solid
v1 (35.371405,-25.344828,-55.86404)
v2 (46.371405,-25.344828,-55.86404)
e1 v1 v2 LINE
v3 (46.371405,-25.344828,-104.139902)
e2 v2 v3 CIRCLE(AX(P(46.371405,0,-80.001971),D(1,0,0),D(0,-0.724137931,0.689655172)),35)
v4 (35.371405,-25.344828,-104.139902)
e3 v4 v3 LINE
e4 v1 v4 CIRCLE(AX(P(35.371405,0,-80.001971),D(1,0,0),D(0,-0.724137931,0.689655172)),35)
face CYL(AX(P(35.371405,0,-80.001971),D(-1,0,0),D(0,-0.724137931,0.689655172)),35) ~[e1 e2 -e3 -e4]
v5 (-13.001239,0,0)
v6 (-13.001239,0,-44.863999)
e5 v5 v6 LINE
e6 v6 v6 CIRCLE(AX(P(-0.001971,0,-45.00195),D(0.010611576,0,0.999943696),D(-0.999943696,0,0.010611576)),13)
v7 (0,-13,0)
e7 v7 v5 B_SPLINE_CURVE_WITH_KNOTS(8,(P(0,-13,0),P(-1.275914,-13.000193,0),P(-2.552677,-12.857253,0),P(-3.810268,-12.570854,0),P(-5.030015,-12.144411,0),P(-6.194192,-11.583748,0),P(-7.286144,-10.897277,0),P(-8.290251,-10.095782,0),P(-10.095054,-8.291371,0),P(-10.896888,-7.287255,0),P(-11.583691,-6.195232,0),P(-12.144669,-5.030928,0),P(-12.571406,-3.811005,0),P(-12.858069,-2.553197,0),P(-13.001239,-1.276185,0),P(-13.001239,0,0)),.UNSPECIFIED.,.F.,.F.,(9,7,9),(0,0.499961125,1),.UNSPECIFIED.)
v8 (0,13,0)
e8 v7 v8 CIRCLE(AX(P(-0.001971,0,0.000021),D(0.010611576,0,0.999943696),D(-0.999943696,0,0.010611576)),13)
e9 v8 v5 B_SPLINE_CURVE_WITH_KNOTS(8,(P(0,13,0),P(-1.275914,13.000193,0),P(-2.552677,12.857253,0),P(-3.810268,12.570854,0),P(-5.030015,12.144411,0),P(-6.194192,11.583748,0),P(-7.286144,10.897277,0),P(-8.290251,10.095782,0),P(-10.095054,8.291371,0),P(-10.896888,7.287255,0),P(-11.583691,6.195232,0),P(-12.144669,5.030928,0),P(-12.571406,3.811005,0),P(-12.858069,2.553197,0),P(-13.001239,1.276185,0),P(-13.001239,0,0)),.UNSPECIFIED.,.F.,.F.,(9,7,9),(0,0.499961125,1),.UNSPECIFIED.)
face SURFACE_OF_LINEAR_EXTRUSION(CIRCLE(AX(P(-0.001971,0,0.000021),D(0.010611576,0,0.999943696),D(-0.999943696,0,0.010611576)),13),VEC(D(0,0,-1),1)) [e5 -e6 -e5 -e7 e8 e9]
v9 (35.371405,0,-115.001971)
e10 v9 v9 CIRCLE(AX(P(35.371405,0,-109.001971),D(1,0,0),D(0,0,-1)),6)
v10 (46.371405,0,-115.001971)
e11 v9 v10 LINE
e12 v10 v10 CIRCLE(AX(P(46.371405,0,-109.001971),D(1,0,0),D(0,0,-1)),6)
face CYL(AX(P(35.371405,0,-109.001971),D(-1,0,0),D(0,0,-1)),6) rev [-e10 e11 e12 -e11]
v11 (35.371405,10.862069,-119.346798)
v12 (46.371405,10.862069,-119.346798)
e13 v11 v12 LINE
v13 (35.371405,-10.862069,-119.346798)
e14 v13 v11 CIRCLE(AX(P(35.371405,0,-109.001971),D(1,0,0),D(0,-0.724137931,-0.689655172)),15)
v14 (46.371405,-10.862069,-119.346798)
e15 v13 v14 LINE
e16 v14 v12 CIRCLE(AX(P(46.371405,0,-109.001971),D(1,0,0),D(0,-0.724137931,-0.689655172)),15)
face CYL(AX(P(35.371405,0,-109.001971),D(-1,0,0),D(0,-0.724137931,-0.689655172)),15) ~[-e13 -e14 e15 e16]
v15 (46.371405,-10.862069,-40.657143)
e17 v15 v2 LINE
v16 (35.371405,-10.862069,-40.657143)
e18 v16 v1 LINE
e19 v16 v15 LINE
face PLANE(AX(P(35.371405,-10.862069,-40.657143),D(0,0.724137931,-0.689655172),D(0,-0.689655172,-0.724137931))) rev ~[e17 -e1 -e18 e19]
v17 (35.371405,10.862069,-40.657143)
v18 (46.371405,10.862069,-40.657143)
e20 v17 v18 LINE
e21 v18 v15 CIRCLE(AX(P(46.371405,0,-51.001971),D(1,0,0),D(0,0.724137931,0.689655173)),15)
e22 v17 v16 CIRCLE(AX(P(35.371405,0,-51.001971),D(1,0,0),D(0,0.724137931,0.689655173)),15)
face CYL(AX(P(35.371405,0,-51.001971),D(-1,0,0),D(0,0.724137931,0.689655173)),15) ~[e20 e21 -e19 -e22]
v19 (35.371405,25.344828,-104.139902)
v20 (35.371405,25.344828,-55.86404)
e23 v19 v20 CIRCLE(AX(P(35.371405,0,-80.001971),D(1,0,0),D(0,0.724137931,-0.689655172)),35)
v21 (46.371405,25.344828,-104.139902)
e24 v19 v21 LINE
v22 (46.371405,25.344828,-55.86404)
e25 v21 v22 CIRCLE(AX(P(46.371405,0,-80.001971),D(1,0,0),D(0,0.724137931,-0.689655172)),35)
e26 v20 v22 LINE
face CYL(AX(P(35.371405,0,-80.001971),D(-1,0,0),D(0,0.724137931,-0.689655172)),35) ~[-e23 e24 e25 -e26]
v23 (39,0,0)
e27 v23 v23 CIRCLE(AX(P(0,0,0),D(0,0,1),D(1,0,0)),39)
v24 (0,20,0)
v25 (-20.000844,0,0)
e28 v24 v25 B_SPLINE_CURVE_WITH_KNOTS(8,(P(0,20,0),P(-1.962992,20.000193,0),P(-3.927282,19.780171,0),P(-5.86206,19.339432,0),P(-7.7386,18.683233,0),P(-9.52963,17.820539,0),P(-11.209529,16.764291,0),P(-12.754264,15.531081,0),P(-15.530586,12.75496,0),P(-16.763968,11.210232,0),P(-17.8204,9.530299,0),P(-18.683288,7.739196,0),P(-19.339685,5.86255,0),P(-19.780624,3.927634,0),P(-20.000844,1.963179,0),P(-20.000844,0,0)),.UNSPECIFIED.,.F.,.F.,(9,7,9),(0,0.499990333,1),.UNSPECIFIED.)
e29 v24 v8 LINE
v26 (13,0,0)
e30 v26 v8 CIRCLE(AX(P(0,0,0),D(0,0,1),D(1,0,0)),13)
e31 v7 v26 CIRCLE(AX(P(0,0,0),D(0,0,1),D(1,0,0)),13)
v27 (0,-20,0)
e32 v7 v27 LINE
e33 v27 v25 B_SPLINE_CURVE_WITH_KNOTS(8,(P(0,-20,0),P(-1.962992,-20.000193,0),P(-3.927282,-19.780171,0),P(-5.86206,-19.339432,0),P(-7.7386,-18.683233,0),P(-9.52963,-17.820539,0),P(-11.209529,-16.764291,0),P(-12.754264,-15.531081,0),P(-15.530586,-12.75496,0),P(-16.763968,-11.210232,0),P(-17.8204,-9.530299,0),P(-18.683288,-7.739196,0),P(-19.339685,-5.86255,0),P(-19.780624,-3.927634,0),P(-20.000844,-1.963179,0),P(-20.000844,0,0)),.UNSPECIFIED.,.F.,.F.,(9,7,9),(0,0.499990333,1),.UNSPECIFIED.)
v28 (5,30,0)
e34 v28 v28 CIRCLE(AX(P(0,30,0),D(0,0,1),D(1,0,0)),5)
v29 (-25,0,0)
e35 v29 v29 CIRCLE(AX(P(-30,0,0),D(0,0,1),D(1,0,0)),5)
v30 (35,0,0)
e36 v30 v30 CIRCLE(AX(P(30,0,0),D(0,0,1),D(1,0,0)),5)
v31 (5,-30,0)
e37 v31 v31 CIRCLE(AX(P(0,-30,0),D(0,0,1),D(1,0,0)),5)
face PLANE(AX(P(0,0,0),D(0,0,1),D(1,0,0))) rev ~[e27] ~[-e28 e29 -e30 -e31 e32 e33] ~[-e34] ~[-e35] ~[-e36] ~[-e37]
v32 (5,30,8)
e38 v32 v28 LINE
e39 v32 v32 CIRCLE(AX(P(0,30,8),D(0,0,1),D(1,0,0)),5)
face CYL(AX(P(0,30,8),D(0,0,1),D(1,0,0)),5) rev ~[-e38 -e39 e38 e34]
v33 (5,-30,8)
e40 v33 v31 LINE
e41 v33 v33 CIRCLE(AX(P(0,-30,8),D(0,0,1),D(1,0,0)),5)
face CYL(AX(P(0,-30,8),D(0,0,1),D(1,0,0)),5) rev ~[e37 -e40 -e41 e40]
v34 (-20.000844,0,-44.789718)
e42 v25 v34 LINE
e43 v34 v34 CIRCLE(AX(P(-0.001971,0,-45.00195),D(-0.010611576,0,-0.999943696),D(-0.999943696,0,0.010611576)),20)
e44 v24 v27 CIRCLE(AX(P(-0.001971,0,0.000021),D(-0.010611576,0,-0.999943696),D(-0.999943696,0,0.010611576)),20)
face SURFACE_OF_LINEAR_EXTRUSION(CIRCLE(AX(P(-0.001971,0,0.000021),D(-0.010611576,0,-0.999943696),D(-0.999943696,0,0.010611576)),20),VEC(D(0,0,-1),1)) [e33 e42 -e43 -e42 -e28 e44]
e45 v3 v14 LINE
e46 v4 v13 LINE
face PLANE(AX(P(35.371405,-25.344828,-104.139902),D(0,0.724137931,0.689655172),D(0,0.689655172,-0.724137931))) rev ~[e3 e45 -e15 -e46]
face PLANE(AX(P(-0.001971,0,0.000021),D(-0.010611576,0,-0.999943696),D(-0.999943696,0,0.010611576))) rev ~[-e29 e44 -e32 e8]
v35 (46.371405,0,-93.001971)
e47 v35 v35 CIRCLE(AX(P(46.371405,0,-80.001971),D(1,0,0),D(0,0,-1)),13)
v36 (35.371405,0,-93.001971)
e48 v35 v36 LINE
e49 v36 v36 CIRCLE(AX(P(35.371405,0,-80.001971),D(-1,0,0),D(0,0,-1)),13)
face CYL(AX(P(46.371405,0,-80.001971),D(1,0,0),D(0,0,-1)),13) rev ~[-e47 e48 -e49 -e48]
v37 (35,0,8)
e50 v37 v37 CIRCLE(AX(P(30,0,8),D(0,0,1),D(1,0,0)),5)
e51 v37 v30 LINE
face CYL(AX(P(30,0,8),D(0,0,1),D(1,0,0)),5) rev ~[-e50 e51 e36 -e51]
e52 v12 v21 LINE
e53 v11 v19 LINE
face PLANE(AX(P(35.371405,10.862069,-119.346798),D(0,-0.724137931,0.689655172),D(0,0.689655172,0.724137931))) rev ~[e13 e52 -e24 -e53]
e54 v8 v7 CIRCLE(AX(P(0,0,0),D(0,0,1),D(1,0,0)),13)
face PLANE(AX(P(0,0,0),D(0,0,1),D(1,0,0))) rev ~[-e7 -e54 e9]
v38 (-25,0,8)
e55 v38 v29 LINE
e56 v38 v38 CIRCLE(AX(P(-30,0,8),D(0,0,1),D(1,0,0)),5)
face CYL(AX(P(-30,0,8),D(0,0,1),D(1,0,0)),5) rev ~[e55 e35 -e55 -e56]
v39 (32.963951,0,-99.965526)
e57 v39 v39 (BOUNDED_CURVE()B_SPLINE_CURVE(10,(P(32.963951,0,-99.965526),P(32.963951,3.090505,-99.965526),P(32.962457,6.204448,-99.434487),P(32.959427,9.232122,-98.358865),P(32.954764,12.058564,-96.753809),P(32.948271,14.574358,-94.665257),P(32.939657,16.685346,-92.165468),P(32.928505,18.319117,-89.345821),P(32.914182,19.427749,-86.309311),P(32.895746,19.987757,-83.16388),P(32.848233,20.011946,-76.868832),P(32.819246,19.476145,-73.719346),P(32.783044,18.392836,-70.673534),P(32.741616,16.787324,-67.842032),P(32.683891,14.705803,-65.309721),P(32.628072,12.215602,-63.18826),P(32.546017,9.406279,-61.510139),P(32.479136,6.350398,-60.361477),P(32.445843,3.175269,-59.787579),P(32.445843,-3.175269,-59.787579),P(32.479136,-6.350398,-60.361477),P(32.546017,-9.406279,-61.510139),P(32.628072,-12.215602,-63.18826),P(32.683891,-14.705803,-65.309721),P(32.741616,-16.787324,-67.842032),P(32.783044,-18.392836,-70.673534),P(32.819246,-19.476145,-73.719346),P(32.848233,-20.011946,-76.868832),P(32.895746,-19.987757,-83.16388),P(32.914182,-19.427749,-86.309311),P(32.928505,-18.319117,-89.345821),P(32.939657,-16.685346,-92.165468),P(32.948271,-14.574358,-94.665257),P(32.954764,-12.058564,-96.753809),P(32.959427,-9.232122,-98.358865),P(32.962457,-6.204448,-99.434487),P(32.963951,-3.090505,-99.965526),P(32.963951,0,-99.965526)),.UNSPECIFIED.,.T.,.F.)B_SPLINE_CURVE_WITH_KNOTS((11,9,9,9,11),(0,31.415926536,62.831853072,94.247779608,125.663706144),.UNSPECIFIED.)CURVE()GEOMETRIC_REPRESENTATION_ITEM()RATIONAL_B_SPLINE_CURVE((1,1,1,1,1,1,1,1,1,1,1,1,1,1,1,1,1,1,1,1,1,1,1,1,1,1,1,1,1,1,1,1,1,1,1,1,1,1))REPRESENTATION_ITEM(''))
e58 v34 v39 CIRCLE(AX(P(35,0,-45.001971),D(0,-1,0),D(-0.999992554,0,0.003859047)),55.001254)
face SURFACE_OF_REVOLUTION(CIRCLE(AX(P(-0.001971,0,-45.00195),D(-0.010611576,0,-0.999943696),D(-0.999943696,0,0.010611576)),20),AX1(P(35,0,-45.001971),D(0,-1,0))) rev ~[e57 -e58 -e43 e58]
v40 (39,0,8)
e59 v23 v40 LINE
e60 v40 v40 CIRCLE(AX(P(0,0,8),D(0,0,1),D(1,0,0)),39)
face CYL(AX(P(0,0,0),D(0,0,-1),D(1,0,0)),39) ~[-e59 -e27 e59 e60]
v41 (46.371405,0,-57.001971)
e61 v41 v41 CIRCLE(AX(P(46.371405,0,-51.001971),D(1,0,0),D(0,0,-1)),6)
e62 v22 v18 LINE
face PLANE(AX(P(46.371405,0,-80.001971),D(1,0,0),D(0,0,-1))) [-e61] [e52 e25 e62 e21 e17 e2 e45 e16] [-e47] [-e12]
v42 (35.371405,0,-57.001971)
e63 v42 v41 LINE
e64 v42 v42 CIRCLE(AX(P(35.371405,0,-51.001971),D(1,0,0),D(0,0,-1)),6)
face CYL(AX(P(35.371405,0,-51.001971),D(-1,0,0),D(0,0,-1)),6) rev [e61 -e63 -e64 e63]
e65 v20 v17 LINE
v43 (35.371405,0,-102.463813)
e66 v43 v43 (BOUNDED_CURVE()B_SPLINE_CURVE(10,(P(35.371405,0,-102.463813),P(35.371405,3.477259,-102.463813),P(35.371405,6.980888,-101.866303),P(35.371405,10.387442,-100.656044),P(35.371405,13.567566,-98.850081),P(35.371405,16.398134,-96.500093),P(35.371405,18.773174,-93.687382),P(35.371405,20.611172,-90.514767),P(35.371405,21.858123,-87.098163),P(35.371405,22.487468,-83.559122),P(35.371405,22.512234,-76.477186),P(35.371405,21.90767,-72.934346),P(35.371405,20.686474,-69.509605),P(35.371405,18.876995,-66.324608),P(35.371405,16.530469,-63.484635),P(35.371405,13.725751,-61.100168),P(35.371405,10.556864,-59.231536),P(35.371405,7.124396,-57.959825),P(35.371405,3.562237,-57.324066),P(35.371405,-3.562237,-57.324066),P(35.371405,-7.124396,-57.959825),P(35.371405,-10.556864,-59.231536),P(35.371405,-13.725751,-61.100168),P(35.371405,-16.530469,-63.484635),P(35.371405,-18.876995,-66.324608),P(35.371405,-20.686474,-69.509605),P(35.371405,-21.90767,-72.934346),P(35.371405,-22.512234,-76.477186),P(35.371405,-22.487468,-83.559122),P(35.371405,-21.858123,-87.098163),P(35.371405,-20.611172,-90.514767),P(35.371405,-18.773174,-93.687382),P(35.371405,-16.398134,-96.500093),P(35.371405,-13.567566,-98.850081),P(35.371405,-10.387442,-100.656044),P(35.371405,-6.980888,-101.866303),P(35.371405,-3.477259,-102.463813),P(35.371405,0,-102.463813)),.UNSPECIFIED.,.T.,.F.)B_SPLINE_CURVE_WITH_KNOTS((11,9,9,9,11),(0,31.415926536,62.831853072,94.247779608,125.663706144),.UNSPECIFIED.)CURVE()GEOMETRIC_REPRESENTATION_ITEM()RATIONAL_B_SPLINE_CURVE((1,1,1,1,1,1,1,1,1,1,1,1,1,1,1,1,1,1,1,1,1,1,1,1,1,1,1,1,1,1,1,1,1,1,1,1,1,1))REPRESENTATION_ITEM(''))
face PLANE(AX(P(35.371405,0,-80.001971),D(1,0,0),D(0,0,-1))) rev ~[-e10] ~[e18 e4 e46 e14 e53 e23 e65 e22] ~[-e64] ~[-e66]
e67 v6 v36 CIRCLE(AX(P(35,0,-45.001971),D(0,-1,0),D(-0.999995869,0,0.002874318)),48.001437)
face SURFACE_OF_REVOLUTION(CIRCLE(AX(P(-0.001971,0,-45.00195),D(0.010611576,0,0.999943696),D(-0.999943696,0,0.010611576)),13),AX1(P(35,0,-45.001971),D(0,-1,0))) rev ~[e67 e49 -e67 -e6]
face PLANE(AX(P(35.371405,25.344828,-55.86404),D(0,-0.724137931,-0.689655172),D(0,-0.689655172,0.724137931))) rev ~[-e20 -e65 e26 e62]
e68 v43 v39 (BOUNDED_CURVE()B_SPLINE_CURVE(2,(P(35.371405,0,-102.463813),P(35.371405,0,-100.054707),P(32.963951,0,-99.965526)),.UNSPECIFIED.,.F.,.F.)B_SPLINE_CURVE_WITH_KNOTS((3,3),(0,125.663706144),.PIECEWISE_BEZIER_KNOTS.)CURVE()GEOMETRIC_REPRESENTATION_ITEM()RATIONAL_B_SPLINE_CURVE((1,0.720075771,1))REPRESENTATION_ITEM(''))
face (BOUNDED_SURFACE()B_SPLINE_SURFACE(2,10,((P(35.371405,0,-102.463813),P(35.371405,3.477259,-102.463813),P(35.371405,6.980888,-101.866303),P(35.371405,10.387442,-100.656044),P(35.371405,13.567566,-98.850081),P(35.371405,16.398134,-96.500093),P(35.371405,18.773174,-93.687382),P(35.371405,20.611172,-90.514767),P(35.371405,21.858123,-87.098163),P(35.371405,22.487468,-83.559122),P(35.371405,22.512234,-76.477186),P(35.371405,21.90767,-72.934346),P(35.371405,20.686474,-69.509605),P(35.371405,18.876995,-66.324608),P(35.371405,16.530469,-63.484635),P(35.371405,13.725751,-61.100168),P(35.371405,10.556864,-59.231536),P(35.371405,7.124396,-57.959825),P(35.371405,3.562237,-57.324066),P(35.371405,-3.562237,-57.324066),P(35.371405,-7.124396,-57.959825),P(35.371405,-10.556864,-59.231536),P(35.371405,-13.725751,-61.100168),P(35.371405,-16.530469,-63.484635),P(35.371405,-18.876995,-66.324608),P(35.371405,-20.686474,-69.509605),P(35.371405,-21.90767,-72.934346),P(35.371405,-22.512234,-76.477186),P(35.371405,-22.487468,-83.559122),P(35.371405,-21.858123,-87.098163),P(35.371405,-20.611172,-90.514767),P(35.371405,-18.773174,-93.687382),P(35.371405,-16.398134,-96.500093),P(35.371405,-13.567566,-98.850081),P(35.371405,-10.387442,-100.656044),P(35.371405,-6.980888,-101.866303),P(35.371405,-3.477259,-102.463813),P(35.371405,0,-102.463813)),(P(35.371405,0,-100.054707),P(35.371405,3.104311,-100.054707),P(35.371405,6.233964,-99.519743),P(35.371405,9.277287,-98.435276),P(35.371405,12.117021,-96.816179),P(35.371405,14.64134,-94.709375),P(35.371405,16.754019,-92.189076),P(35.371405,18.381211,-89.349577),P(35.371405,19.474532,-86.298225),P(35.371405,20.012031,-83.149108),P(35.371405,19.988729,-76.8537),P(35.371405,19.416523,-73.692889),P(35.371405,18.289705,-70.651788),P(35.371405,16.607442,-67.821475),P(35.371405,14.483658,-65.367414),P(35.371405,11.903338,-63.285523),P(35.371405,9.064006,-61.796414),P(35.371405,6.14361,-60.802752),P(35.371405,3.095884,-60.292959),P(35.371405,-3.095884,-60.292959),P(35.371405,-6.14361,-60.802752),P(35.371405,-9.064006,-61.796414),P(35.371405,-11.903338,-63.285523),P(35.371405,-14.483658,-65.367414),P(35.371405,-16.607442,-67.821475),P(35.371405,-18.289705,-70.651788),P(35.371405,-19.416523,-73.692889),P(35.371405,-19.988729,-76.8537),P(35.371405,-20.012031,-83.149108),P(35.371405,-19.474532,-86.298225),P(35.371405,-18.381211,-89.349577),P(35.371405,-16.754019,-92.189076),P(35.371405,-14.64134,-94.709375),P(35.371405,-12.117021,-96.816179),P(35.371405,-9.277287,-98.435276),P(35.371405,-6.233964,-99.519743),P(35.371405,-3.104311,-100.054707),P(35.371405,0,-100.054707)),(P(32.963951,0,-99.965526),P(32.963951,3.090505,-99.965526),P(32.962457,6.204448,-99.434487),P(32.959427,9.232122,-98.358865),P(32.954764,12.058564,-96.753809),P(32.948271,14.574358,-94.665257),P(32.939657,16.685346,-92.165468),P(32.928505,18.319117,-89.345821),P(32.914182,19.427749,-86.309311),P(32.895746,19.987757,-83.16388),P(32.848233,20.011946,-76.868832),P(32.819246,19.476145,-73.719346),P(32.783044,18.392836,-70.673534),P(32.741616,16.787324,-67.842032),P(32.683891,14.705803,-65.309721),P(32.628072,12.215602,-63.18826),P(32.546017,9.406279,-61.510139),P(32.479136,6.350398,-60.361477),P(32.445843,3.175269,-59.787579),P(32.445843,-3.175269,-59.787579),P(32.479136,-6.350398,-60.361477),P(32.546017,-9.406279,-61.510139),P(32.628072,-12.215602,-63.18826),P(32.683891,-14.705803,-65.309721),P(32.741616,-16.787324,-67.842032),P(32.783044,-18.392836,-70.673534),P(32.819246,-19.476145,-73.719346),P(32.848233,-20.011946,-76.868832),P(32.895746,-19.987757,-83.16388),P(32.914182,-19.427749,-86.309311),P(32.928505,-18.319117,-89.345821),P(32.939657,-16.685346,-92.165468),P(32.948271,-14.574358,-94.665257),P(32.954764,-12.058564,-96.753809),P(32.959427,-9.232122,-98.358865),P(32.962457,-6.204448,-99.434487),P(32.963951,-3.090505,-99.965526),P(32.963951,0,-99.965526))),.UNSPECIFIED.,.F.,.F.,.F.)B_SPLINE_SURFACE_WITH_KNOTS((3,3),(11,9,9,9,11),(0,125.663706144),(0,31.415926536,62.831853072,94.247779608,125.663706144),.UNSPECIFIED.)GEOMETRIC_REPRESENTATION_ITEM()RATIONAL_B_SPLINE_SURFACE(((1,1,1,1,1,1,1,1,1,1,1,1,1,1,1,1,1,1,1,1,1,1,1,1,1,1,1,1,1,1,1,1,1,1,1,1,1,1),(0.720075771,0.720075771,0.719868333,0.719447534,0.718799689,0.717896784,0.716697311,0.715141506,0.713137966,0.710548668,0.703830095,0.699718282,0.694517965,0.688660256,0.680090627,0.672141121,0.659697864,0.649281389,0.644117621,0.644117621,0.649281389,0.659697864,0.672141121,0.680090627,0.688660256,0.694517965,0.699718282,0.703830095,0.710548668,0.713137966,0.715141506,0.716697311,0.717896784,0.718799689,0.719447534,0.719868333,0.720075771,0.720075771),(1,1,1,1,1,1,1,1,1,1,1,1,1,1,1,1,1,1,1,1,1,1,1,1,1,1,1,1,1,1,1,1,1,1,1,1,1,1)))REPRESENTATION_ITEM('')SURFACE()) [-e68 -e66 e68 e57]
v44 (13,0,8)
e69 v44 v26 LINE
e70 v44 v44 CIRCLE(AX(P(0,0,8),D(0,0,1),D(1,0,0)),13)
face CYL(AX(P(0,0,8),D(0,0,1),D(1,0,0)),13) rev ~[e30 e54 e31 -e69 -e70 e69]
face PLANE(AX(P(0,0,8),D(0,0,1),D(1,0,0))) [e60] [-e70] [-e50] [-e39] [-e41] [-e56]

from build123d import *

# Parameters (mm, degrees)
ROUND_FLANGE_SKETCH_R       = 39
ROUND_FLANGE_78_DEPTH       = 8
ROUND_FLANGE_HOLES_SKETCH_R = 5
ROUND_FLANGE_HOLES_4X_DEPTH = 8
ELBOW_PROFILE_SKETCH_R      = 20
ELBOW_PROFILE_SKETCH_R_2    = 13
ROUND_FLANGE_BORE_SKETCH_R  = 13
ROUND_FLANGE_BORE_26_DEPTH  = 8
OVAL_FLANGE_SKETCH_R        = 6
OVAL_FLANGE_DEPTH           = 11
OVAL_FLANGE_BORE_SKETCH_R   = 13
OVAL_FLANGE_BORE_26_DEPTH   = 11
FLANGE_FILLETS_R2_5_R       = 2.5


with BuildPart() as part:
    # Round Flange Sketch → Round Flange Ø78 (new body)
    with BuildSketch(Plane.XY):
        Circle(ROUND_FLANGE_SKETCH_R)
    extrude(amount=ROUND_FLANGE_78_DEPTH)

    # Round Flange Holes Sketch → Round Flange Holes 4x (cut)
    with BuildSketch(Plane.XY.offset(8)):
        with Locations((0, 30)):
            Circle(ROUND_FLANGE_HOLES_SKETCH_R)
        with Locations((30, 0)):
            Circle(ROUND_FLANGE_HOLES_SKETCH_R)
        with Locations((0, -30)):
            Circle(ROUND_FLANGE_HOLES_SKETCH_R)
        with Locations((-30, 0)):
            Circle(ROUND_FLANGE_HOLES_SKETCH_R)
    extrude(amount=-ROUND_FLANGE_HOLES_4X_DEPTH, mode=Mode.SUBTRACT)

    # Elbow Tube Ø40: sweep along a path in Elbow Path Sketch
    with BuildLine(Plane(origin=(0, 0, 0), x_dir=(1, 0, 0), z_dir=(0, 1, 0))) as elbow_tube_40_path:
        Line((0, 0), (0, 45.001970653))
        ThreePointArc((0, 45.001970653), (10.38292443, 69.88167303), (35.371405165, 80))
    # Elbow Profile Sketch → Elbow Tube Ø40 (sweep)
    with BuildSketch(Plane(origin=(35.371405165, 0, 0), x_dir=(0, 0, -1), z_dir=(1, 0, 0))):
        with Locations((80.001970653, 0)):
            Circle(ELBOW_PROFILE_SKETCH_R)
        with Locations((80.001970653, 0)):
            Circle(ELBOW_PROFILE_SKETCH_R_2, mode=Mode.SUBTRACT)
    sweep(path=elbow_tube_40_path.line)

    # Round Flange Bore Sketch → Round Flange Bore Ø26 (cut)
    with BuildSketch(Plane.XY.offset(8)):
        Circle(ROUND_FLANGE_BORE_SKETCH_R)
    extrude(amount=-ROUND_FLANGE_BORE_26_DEPTH, mode=Mode.SUBTRACT)

    # Oval Flange Sketch → Oval Flange (add)
    with BuildSketch(Plane(origin=(35.371405165, 0, 0), x_dir=(0, 0, -1), z_dir=(1, 0, 0))):
        with BuildLine():
            Line((119.346798239, 10.862068966), (104.139901687, 25.344827586))
            ThreePointArc((104.139901687, 25.344827586), (80.001970653, 35), (55.864039618, 25.344827586))
            Line((55.864039618, 25.344827586), (40.657143066, 10.862068966))
            ThreePointArc((40.657143066, 10.862068966), (36.001970653, 0), (40.657143066, -10.862068966))
            Line((40.657143066, -10.862068966), (55.864039618, -25.344827586))
            ThreePointArc((55.864039618, -25.344827586), (80.001970653, -35), (104.139901687, -25.344827586))
            Line((104.139901687, -25.344827586), (119.346798239, -10.862068966))
            ThreePointArc((119.346798239, -10.862068966), (124.001970653, 0), (119.346798239, 10.862068966))
        make_face()
        with Locations((51.001970653, 0)):
            Circle(OVAL_FLANGE_SKETCH_R, mode=Mode.SUBTRACT)
        with Locations((109.001970653, 0)):
            Circle(OVAL_FLANGE_SKETCH_R, mode=Mode.SUBTRACT)
    extrude(amount=OVAL_FLANGE_DEPTH)

    # Oval Flange Bore Sketch → Oval Flange Bore Ø26 (cut)
    with BuildSketch(Plane(origin=(46.371405165, 0, 0), x_dir=(0, 0, -1), z_dir=(1, 0, 0))):
        with Locations((80.001970653, 0)):
            Circle(OVAL_FLANGE_BORE_SKETCH_R)
    extrude(amount=-OVAL_FLANGE_BORE_26_DEPTH, mode=Mode.SUBTRACT)

    # Flange Fillets R2.5
    flange_fillets_r2_5_edges = [part.edges().sort_by_distance(p)[0] for p in [
        (35.371405165, 0, -60.001970653),
    ]]
    fillet(flange_fillets_r2_5_edges, radius=FLANGE_FILLETS_R2_5_R)


solid = part.part
